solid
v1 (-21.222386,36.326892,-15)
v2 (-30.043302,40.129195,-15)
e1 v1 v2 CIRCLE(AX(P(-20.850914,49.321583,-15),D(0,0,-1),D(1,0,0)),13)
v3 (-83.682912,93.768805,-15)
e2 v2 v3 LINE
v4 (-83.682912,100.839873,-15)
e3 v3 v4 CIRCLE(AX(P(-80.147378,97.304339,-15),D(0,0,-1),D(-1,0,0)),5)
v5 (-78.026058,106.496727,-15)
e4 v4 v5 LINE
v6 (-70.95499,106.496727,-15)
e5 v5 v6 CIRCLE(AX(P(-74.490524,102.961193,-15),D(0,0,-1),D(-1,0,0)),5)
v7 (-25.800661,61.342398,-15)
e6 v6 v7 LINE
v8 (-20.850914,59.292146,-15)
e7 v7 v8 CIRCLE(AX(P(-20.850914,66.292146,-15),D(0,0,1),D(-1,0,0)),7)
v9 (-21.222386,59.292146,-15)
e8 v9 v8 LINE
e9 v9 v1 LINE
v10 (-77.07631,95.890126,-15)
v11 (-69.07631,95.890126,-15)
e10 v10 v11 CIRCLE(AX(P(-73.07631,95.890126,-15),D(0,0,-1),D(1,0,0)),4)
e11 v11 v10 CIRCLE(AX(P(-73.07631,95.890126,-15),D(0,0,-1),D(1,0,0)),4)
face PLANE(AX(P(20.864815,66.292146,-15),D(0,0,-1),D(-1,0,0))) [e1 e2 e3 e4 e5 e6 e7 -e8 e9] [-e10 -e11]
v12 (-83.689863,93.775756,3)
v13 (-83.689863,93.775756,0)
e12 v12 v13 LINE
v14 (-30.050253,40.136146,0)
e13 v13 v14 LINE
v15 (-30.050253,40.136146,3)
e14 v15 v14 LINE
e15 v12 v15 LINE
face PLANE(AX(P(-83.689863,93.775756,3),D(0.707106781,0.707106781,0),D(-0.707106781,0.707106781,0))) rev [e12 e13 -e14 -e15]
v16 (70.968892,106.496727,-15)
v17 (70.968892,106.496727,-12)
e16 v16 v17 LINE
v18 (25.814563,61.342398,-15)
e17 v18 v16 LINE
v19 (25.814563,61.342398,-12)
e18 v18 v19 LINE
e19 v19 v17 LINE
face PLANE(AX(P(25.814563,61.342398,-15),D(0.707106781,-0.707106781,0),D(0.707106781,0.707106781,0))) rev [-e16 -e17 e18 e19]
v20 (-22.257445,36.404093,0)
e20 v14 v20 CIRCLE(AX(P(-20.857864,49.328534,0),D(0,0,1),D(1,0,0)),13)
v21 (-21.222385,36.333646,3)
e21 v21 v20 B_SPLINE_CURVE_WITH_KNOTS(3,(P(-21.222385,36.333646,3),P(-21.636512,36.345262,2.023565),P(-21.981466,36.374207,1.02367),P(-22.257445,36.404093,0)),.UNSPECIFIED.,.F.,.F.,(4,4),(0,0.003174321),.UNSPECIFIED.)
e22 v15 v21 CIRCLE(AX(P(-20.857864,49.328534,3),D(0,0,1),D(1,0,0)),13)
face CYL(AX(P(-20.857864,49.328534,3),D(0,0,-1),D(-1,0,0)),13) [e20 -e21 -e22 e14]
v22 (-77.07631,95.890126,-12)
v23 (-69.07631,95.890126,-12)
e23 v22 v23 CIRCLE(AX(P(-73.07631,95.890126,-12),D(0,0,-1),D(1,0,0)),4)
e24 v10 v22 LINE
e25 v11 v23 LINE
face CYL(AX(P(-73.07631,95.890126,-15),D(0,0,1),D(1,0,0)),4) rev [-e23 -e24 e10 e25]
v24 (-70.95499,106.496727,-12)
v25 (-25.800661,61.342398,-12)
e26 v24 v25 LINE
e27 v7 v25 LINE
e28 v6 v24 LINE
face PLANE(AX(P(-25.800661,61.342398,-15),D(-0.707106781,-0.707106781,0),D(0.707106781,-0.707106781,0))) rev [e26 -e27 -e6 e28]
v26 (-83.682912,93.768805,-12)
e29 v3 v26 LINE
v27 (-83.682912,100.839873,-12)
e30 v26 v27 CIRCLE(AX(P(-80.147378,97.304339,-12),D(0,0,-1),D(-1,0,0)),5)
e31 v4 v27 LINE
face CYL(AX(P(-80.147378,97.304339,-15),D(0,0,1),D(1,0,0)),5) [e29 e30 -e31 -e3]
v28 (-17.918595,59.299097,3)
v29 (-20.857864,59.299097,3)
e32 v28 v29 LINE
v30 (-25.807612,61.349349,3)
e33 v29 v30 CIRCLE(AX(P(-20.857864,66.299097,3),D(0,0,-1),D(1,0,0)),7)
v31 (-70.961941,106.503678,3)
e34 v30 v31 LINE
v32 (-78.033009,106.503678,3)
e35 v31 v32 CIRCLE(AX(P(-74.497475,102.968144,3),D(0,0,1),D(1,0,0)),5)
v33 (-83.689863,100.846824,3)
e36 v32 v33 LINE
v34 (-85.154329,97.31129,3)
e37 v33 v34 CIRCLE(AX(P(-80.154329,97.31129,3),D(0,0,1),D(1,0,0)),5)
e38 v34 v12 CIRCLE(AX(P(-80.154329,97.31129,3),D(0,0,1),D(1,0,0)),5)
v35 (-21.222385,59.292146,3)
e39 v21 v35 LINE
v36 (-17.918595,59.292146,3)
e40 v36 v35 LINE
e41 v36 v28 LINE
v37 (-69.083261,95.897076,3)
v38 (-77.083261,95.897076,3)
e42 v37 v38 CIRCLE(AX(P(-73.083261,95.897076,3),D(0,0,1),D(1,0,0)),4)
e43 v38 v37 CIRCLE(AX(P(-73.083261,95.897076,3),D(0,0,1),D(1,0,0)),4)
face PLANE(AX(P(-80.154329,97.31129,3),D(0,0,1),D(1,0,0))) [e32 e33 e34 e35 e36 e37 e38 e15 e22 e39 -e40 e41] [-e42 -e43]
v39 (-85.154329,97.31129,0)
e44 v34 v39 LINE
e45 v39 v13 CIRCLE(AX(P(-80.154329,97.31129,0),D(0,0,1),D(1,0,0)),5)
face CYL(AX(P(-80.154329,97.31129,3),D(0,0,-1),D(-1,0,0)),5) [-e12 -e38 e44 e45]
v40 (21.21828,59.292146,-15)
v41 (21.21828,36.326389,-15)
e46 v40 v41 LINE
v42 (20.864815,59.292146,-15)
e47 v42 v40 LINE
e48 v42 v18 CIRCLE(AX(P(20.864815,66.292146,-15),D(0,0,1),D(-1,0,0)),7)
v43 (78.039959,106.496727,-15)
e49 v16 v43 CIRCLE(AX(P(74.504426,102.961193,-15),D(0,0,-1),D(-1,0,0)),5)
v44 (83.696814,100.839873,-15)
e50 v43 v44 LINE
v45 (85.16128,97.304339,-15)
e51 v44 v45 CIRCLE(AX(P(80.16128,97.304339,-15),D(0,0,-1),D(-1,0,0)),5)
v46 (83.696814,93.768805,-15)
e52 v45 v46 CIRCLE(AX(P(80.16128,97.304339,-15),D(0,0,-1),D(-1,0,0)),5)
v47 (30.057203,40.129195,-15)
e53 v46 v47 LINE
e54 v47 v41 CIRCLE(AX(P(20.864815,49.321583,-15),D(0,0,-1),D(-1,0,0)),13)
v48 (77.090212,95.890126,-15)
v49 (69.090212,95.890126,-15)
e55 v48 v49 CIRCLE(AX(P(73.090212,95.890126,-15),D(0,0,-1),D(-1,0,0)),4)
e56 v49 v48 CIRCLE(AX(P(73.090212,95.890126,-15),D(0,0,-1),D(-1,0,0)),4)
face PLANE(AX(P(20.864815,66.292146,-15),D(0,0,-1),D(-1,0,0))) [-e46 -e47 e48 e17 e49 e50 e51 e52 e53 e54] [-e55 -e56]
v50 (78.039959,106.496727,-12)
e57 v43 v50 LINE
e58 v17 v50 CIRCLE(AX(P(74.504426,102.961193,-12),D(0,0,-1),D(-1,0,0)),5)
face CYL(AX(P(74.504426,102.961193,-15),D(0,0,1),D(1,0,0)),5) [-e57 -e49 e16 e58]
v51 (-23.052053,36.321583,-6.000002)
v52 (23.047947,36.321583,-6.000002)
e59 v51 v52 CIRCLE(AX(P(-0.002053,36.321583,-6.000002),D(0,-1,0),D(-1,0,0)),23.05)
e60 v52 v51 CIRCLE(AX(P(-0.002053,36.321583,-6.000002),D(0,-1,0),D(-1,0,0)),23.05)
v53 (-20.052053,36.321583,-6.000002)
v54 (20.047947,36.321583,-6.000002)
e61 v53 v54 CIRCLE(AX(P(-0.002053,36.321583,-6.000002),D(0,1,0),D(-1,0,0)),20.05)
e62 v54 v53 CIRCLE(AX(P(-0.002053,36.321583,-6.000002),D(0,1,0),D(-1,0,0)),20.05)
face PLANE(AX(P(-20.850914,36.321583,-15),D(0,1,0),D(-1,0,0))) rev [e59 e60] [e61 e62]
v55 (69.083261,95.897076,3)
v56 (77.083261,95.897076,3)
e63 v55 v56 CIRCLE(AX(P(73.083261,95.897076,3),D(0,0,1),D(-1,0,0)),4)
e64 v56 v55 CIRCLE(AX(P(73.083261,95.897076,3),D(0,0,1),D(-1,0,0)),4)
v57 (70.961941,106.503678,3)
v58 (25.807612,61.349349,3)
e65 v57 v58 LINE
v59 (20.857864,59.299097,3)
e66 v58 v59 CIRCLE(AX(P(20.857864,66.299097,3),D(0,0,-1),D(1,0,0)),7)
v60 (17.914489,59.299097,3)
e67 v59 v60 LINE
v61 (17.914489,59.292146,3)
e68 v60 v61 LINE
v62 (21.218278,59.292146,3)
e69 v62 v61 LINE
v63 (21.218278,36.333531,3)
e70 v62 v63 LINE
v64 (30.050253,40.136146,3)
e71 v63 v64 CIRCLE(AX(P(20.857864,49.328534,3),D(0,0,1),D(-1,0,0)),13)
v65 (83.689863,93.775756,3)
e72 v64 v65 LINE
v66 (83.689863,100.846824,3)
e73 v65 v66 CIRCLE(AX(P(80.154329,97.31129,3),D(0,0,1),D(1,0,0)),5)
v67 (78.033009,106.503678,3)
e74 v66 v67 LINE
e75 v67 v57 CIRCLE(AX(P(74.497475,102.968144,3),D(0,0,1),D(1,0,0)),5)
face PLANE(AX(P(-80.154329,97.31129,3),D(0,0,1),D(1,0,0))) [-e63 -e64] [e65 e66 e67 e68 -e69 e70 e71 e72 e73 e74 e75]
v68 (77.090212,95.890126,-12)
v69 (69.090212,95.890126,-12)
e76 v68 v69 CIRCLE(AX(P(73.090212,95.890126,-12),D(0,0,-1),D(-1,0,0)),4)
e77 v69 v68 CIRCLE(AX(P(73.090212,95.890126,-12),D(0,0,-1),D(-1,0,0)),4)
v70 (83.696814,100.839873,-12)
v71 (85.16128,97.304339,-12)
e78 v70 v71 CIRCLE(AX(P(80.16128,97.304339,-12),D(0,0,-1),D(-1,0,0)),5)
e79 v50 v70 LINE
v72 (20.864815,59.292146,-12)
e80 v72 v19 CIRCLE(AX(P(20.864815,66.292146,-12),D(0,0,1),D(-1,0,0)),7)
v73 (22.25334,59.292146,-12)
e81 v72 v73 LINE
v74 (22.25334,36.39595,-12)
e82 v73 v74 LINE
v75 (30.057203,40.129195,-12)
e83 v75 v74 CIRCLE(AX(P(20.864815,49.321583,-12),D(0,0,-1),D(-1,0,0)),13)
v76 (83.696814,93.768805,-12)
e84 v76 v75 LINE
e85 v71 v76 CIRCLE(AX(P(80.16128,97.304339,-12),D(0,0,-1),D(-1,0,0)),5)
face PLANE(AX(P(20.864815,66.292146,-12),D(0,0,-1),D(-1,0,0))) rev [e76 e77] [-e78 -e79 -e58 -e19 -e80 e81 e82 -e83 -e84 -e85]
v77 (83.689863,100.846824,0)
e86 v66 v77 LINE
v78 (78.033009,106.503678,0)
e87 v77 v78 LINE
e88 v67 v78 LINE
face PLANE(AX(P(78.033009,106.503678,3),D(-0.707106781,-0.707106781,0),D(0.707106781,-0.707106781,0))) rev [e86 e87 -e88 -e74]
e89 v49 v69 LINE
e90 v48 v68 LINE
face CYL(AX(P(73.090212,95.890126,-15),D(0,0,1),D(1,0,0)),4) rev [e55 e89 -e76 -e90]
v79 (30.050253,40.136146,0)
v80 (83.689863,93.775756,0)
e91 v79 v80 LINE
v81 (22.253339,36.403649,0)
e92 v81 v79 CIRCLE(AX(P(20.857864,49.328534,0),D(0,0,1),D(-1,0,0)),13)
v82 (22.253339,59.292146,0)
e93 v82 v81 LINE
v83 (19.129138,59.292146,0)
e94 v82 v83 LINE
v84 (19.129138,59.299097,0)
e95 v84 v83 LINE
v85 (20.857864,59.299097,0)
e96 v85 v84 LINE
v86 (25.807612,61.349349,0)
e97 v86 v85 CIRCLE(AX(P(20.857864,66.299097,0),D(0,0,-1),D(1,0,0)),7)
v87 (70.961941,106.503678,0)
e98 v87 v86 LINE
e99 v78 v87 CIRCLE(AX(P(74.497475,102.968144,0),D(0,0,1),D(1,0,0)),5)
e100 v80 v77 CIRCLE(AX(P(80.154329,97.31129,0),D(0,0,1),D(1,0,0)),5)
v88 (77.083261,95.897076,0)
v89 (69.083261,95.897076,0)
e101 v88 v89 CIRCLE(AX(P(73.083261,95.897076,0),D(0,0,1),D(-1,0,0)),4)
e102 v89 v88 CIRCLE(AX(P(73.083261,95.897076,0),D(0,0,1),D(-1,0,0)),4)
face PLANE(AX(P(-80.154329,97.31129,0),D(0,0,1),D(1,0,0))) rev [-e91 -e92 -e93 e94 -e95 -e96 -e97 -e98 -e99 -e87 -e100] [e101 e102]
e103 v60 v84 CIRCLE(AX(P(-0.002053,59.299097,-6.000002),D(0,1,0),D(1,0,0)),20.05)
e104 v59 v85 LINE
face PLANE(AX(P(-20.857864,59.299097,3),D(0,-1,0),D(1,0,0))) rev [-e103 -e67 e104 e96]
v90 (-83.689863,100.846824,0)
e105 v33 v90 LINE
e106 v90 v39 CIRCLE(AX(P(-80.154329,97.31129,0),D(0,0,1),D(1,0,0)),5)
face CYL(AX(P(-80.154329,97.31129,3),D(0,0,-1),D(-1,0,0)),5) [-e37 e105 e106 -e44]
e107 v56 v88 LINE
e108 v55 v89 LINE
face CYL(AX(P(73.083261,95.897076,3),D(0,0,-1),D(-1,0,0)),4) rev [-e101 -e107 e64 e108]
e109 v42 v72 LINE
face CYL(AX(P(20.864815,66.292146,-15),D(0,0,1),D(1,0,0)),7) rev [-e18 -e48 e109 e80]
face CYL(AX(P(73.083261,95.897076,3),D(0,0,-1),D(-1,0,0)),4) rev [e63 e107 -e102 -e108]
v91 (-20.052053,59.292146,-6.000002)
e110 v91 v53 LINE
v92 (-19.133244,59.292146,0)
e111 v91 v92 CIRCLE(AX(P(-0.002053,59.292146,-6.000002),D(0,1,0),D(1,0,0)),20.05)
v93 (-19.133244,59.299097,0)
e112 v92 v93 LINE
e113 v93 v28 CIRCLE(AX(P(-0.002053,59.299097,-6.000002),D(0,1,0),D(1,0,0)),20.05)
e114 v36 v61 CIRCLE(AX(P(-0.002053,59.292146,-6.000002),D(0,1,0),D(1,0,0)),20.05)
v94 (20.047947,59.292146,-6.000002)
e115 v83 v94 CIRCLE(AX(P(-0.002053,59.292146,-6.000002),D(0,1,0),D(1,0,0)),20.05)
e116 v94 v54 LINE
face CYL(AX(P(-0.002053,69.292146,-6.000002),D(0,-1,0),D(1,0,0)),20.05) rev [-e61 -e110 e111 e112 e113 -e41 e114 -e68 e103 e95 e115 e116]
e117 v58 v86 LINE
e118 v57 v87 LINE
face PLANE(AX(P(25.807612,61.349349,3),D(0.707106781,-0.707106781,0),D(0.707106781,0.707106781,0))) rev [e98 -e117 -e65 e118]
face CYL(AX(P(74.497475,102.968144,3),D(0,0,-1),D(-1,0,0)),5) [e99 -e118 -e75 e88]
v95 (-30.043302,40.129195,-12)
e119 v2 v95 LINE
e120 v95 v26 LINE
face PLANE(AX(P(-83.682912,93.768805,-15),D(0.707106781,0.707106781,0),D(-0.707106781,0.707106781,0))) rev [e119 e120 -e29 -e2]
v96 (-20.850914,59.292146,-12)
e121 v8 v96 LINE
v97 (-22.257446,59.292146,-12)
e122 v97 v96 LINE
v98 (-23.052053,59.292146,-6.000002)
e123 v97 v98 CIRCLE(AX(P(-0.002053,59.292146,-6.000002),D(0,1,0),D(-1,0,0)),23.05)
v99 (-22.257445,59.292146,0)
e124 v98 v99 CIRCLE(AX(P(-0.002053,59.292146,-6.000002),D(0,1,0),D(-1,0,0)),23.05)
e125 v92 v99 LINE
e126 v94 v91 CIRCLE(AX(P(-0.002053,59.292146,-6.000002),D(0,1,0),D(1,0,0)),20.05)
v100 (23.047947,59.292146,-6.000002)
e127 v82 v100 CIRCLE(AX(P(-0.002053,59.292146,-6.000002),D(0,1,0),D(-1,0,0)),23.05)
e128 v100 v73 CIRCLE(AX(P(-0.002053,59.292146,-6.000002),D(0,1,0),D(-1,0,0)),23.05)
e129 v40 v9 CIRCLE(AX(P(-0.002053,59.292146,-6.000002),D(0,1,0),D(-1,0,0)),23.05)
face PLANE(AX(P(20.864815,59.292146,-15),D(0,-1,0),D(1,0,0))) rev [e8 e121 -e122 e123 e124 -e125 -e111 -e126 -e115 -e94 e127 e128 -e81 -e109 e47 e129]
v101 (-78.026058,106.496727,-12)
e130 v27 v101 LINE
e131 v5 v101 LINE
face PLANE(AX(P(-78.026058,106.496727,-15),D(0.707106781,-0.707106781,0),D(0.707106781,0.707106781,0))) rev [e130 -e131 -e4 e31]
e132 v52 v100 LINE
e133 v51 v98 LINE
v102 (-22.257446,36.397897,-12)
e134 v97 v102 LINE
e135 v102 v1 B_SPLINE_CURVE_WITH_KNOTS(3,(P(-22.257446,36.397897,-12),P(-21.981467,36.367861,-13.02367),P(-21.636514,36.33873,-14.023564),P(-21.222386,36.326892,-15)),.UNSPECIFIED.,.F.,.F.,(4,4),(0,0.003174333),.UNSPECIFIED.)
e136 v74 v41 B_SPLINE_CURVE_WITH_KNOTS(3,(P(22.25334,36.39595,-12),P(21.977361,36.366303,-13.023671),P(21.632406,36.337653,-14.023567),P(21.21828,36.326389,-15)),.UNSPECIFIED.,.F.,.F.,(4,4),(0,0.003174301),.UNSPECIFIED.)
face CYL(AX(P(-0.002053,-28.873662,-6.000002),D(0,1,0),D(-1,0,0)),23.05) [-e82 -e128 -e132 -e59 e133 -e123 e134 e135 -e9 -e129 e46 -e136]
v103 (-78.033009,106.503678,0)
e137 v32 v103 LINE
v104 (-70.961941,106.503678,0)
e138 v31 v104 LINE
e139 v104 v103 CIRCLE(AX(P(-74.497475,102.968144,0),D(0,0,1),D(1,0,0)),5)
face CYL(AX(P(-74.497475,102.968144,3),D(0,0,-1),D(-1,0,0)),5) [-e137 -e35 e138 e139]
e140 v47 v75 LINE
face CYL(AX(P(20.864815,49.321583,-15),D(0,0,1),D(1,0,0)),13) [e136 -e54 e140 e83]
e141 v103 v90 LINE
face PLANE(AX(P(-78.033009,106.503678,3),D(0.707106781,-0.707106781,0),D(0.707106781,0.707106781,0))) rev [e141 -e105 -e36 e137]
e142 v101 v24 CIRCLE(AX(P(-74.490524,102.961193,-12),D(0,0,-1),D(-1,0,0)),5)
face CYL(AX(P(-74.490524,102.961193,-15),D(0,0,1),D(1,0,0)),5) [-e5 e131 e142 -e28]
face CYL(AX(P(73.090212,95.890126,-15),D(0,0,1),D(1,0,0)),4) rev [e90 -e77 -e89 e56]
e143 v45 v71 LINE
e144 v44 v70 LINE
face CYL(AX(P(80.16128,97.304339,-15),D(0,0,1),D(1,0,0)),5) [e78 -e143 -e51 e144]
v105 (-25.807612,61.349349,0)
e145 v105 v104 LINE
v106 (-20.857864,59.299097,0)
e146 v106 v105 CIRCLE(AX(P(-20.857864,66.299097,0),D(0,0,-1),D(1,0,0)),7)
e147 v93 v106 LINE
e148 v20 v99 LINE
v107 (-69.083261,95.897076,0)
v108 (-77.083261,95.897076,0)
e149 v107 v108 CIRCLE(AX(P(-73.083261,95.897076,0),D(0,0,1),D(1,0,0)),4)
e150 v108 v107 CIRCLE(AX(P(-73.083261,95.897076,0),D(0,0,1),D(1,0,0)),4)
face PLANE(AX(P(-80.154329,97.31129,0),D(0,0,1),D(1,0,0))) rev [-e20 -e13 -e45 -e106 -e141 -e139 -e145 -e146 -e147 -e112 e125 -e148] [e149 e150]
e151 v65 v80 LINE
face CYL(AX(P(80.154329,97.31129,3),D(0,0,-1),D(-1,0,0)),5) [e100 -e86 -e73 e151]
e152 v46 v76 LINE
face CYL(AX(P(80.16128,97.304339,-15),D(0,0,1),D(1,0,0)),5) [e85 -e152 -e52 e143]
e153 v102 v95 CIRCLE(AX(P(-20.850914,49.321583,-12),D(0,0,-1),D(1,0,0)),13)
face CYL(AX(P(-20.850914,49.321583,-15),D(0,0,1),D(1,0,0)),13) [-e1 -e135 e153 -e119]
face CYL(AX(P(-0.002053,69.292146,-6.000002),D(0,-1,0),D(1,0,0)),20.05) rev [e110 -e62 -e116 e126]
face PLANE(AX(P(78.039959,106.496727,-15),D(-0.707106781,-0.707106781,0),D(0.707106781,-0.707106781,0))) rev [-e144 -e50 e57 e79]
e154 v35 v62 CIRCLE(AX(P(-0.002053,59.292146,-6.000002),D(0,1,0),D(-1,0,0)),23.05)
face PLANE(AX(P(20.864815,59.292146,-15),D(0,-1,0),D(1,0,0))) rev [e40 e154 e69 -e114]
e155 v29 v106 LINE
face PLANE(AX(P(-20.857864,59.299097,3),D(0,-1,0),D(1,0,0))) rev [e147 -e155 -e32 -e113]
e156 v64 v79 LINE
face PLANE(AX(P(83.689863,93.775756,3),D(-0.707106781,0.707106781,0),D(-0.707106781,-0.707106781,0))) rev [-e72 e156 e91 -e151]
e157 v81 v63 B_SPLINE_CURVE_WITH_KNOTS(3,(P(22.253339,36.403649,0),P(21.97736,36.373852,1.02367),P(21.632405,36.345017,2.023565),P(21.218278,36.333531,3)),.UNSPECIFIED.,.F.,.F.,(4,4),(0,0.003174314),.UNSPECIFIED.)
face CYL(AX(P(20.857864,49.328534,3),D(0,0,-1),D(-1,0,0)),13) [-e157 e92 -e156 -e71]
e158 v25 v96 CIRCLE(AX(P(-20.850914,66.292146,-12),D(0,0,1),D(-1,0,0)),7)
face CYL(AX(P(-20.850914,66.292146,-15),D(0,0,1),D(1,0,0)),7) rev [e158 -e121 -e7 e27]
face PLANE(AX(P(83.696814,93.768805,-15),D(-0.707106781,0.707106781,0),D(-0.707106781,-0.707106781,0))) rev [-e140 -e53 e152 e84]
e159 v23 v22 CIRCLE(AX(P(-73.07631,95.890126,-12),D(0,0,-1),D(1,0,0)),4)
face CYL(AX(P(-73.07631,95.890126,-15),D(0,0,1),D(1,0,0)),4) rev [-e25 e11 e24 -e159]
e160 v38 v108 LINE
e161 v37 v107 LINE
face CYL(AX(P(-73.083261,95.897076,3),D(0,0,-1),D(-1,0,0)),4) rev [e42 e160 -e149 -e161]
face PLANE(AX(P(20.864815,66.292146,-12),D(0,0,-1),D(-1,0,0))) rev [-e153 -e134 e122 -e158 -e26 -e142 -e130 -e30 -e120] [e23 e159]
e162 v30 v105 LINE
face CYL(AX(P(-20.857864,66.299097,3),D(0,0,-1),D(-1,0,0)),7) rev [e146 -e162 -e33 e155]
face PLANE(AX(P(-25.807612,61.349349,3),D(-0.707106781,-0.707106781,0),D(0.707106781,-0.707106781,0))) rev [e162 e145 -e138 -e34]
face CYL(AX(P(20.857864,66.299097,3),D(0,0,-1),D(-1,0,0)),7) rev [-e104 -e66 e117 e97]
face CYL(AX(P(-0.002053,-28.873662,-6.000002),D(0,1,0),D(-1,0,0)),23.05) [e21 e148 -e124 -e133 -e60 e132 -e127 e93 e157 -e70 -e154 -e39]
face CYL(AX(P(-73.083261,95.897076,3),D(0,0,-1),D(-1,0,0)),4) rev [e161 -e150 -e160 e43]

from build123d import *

# Parameters (mm, degrees)
SKETCH1_R               = 4
BOSS_EXTRU_1_DEPTH      = 3
SKETCH2_R               = 4
BOSS_EXTRU_2_DEPTH      = 3
CUT_EXTRUDE1_DEPTH      = 10
CUT_EXTRUDE1_DEPTH_BACK = 100.231025361
SKETCH3_R               = 20.05
BOSS_EXTRU_3_REACH      = 101.231
SKETCH5_R               = 23.05
SKETCH5_R_2             = 20.05


with BuildPart() as part:
    # Sketch1 → Boss.-Extru.1 (new body)
    with BuildSketch(Plane.XY):
        with BuildLine():
            Line((-83.689862838, 93.775756105), (-30.050252532, 40.136145798))
            ThreePointArc((-30.050252532, 40.136145798), (-25.832748997, 37.318100031), (-20.857864376, 36.328533954))
            Line((-20.857864376, 36.328533954), (20.857864376, 36.328533954))
            ThreePointArc((20.857864376, 36.328533954), (25.832748997, 37.318100031), (30.050252532, 40.136145798))
            Line((30.050252532, 40.136145798), (83.689862838, 93.775756105))
            ThreePointArc((83.689862838, 93.775756105), (85.154328933, 97.311290011), (83.689862838, 100.846823917))
            Line((83.689862838, 100.846823917), (78.033008589, 106.503678166))
            ThreePointArc((78.033008589, 106.503678166), (74.497474683, 107.96814426), (70.961940777, 106.503678166))
            Line((70.961940777, 106.503678166), (25.807611845, 61.349349234))
            ThreePointArc((25.807611845, 61.349349234), (23.536648403, 59.831939975), (20.857864376, 59.299096702))
            Line((20.857864376, 59.299096702), (-20.857864376, 59.299096702))
            ThreePointArc((-20.857864376, 59.299096702), (-23.536648403, 59.831939975), (-25.807611845, 61.349349234))
            Line((-25.807611845, 61.349349234), (-70.961940777, 106.503678166))
            ThreePointArc((-70.961940777, 106.503678166), (-74.497474683, 107.96814426), (-78.033008589, 106.503678166))
            Line((-78.033008589, 106.503678166), (-83.689862838, 100.846823917))
            ThreePointArc((-83.689862838, 100.846823917), (-85.154328933, 97.311290011), (-83.689862838, 93.775756105))
        make_face()
        with Locations((-73.083261121, 95.897076449)):
            Circle(SKETCH1_R, mode=Mode.SUBTRACT)
        with Locations(Location((73.083261121, 95.897076449, 0), (0, 0, 180))):
            Circle(SKETCH1_R, mode=Mode.SUBTRACT)
    extrude(amount=BOSS_EXTRU_1_DEPTH)


with BuildPart() as body_2:
    # Sketch2 → Boss.-Extru.2 (new body)
    with BuildSketch(Plane(origin=(0, 0, -12), x_dir=(-1, 0, 0), z_dir=(0, 0, -1))):
        with BuildLine():
            Line((-25.814562691, 61.342398387), (-70.968891623, 106.49672732))
            ThreePointArc((-70.968891623, 106.49672732), (-74.504425529, 107.961193414), (-78.039959435, 106.49672732))
            Line((-78.039959435, 106.49672732), (-83.696813685, 100.839873071))
            ThreePointArc((-83.696813685, 100.839873071), (-85.161279779, 97.304339165), (-83.696813685, 93.768805259))
            Line((-83.696813685, 93.768805259), (-30.057203378, 40.129194952))
            ThreePointArc((-30.057203378, 40.129194952), (-25.839699843, 37.311149185), (-20.864815223, 36.321583107))
            Line((-20.864815223, 36.321583107), (20.85091353, 36.321583107))
            ThreePointArc((20.85091353, 36.321583107), (25.825798151, 37.311149185), (30.043301685, 40.129194952))
            Line((30.043301685, 40.129194952), (83.682911992, 93.768805259))
            ThreePointArc((83.682911992, 93.768805259), (85.147378086, 97.304339165), (83.682911992, 100.839873071))
            Line((83.682911992, 100.839873071), (78.026057743, 106.49672732))
            ThreePointArc((78.026057743, 106.49672732), (74.490523837, 107.961193414), (70.954989931, 106.49672732))
            Line((70.954989931, 106.49672732), (25.800660998, 61.342398387))
            ThreePointArc((25.800660998, 61.342398387), (23.529697556, 59.824989128), (20.85091353, 59.292145856))
            Line((20.85091353, 59.292145856), (-20.864815223, 59.292145856))
            ThreePointArc((-20.864815223, 59.292145856), (-23.543599249, 59.824989128), (-25.814562691, 61.342398387))
        make_face()
        with Locations((-73.090211967, 95.890125602)):
            Circle(SKETCH2_R, mode=Mode.SUBTRACT)
        with Locations(Location((73.076310274, 95.890125602, 0), (0, 0, 180))):
            Circle(SKETCH2_R, mode=Mode.SUBTRACT)
    extrude(amount=BOSS_EXTRU_2_DEPTH)


with BuildPart() as cut_extrude1_tool:
    # Sketch3 → Cut-Extrude1 (new, two sides: drawn at the far end of the back side and taken through both)
    with BuildSketch(Plane(origin=(0, 59.292145856, 0), x_dir=(1, 0, 0), z_dir=(0, 1, 0)).offset(-CUT_EXTRUDE1_DEPTH_BACK)):
        with Locations((-0.00205312, 6.000001678)):
            Circle(SKETCH3_R)
    extrude(amount=CUT_EXTRUDE1_DEPTH + CUT_EXTRUDE1_DEPTH_BACK)


with BuildPart() as part_1:
    add(part.part)

    # Cut-Extrude1: cut by cut_extrude1_tool
    add(cut_extrude1_tool.part, mode=Mode.SUBTRACT)


with BuildPart() as body_2_1:
    add(body_2.part)

    # Cut-Extrude1: cut by cut_extrude1_tool
    add(cut_extrude1_tool.part, mode=Mode.SUBTRACT)


with BuildPart() as cut_extrude1_piece_1:
    # of the separate pieces the step leaves, piece 1, a body of its own (cut_extrude1_pieces)
    add(part_1.part.solids().sort_by_distance((19.129138162, 36.328533954, 0))[0])


with BuildPart() as cut_extrude1_piece_2:
    # of the separate pieces the step leaves, piece 2, a body of its own (cut_extrude1_pieces)
    add(part_1.part.solids().sort_by_distance((-83.689862838, 93.775756105, 0))[0])


with BuildPart() as cut_extrude1_piece_1_of_body_2:
    # of the separate pieces the step leaves, piece 1, a body of its own (cut_extrude1_pieces_of_body_2)
    add(body_2_1.part.solids().sort_by_distance((25.814562691, 61.342398387, -12))[0])


with BuildPart() as cut_extrude1_piece_2_of_body_2:
    # of the separate pieces the step leaves, piece 2, a body of its own (cut_extrude1_pieces_of_body_2)
    add(body_2_1.part.solids().sort_by_distance((-20.85091353, 59.292145856, -12))[0])

    # Boss.-Extru.3: up to this face of the body (flat: up to its plane)
    boss_extru_3_end = Plane(cut_extrude1_piece_2_of_body_2.part.faces().sort_by_distance((-19.684947548, 36.321583107, -13.633103381))[0])
    # Sketch5 → Boss.-Extru.3 (add, up to the picked face)
    with BuildSketch(Plane(origin=(0, 59.292145856, 0), x_dir=(1, 0, 0), z_dir=(0, 1, 0)), mode=Mode.PRIVATE) as boss_extru_3_sk1:
        with Locations(Location((-0.00205312, 6.000001678, 0), (0, 0, 180))):
            Circle(SKETCH5_R)
        with Locations(Location((-0.00205312, 6.000001678, 0), (0, 0, 342.587320704))):
            Circle(SKETCH5_R_2, mode=Mode.SUBTRACT)
    boss_extru_3_tool1 = split(extrude(boss_extru_3_sk1.sketch, amount=-BOSS_EXTRU_3_REACH, mode=Mode.PRIVATE), bisect_by=boss_extru_3_end, keep=Keep.BOTH, mode=Mode.PRIVATE)

    add(cut_extrude1_piece_1.part)  # Boss.-Extru.3 merges Cut-Extrude1 piece 1

    add(cut_extrude1_piece_2.part)  # Boss.-Extru.3 merges Cut-Extrude1 piece 2

    add(cut_extrude1_piece_1_of_body_2.part)  # Boss.-Extru.3 merges Cut-Extrude1 piece 1 of body 2
    add(boss_extru_3_tool1.solids().sort_by(Axis((22.395994, 59.292146, -6.000002), (0, -1, 0)))[0])


solid = cut_extrude1_piece_2_of_body_2.part
